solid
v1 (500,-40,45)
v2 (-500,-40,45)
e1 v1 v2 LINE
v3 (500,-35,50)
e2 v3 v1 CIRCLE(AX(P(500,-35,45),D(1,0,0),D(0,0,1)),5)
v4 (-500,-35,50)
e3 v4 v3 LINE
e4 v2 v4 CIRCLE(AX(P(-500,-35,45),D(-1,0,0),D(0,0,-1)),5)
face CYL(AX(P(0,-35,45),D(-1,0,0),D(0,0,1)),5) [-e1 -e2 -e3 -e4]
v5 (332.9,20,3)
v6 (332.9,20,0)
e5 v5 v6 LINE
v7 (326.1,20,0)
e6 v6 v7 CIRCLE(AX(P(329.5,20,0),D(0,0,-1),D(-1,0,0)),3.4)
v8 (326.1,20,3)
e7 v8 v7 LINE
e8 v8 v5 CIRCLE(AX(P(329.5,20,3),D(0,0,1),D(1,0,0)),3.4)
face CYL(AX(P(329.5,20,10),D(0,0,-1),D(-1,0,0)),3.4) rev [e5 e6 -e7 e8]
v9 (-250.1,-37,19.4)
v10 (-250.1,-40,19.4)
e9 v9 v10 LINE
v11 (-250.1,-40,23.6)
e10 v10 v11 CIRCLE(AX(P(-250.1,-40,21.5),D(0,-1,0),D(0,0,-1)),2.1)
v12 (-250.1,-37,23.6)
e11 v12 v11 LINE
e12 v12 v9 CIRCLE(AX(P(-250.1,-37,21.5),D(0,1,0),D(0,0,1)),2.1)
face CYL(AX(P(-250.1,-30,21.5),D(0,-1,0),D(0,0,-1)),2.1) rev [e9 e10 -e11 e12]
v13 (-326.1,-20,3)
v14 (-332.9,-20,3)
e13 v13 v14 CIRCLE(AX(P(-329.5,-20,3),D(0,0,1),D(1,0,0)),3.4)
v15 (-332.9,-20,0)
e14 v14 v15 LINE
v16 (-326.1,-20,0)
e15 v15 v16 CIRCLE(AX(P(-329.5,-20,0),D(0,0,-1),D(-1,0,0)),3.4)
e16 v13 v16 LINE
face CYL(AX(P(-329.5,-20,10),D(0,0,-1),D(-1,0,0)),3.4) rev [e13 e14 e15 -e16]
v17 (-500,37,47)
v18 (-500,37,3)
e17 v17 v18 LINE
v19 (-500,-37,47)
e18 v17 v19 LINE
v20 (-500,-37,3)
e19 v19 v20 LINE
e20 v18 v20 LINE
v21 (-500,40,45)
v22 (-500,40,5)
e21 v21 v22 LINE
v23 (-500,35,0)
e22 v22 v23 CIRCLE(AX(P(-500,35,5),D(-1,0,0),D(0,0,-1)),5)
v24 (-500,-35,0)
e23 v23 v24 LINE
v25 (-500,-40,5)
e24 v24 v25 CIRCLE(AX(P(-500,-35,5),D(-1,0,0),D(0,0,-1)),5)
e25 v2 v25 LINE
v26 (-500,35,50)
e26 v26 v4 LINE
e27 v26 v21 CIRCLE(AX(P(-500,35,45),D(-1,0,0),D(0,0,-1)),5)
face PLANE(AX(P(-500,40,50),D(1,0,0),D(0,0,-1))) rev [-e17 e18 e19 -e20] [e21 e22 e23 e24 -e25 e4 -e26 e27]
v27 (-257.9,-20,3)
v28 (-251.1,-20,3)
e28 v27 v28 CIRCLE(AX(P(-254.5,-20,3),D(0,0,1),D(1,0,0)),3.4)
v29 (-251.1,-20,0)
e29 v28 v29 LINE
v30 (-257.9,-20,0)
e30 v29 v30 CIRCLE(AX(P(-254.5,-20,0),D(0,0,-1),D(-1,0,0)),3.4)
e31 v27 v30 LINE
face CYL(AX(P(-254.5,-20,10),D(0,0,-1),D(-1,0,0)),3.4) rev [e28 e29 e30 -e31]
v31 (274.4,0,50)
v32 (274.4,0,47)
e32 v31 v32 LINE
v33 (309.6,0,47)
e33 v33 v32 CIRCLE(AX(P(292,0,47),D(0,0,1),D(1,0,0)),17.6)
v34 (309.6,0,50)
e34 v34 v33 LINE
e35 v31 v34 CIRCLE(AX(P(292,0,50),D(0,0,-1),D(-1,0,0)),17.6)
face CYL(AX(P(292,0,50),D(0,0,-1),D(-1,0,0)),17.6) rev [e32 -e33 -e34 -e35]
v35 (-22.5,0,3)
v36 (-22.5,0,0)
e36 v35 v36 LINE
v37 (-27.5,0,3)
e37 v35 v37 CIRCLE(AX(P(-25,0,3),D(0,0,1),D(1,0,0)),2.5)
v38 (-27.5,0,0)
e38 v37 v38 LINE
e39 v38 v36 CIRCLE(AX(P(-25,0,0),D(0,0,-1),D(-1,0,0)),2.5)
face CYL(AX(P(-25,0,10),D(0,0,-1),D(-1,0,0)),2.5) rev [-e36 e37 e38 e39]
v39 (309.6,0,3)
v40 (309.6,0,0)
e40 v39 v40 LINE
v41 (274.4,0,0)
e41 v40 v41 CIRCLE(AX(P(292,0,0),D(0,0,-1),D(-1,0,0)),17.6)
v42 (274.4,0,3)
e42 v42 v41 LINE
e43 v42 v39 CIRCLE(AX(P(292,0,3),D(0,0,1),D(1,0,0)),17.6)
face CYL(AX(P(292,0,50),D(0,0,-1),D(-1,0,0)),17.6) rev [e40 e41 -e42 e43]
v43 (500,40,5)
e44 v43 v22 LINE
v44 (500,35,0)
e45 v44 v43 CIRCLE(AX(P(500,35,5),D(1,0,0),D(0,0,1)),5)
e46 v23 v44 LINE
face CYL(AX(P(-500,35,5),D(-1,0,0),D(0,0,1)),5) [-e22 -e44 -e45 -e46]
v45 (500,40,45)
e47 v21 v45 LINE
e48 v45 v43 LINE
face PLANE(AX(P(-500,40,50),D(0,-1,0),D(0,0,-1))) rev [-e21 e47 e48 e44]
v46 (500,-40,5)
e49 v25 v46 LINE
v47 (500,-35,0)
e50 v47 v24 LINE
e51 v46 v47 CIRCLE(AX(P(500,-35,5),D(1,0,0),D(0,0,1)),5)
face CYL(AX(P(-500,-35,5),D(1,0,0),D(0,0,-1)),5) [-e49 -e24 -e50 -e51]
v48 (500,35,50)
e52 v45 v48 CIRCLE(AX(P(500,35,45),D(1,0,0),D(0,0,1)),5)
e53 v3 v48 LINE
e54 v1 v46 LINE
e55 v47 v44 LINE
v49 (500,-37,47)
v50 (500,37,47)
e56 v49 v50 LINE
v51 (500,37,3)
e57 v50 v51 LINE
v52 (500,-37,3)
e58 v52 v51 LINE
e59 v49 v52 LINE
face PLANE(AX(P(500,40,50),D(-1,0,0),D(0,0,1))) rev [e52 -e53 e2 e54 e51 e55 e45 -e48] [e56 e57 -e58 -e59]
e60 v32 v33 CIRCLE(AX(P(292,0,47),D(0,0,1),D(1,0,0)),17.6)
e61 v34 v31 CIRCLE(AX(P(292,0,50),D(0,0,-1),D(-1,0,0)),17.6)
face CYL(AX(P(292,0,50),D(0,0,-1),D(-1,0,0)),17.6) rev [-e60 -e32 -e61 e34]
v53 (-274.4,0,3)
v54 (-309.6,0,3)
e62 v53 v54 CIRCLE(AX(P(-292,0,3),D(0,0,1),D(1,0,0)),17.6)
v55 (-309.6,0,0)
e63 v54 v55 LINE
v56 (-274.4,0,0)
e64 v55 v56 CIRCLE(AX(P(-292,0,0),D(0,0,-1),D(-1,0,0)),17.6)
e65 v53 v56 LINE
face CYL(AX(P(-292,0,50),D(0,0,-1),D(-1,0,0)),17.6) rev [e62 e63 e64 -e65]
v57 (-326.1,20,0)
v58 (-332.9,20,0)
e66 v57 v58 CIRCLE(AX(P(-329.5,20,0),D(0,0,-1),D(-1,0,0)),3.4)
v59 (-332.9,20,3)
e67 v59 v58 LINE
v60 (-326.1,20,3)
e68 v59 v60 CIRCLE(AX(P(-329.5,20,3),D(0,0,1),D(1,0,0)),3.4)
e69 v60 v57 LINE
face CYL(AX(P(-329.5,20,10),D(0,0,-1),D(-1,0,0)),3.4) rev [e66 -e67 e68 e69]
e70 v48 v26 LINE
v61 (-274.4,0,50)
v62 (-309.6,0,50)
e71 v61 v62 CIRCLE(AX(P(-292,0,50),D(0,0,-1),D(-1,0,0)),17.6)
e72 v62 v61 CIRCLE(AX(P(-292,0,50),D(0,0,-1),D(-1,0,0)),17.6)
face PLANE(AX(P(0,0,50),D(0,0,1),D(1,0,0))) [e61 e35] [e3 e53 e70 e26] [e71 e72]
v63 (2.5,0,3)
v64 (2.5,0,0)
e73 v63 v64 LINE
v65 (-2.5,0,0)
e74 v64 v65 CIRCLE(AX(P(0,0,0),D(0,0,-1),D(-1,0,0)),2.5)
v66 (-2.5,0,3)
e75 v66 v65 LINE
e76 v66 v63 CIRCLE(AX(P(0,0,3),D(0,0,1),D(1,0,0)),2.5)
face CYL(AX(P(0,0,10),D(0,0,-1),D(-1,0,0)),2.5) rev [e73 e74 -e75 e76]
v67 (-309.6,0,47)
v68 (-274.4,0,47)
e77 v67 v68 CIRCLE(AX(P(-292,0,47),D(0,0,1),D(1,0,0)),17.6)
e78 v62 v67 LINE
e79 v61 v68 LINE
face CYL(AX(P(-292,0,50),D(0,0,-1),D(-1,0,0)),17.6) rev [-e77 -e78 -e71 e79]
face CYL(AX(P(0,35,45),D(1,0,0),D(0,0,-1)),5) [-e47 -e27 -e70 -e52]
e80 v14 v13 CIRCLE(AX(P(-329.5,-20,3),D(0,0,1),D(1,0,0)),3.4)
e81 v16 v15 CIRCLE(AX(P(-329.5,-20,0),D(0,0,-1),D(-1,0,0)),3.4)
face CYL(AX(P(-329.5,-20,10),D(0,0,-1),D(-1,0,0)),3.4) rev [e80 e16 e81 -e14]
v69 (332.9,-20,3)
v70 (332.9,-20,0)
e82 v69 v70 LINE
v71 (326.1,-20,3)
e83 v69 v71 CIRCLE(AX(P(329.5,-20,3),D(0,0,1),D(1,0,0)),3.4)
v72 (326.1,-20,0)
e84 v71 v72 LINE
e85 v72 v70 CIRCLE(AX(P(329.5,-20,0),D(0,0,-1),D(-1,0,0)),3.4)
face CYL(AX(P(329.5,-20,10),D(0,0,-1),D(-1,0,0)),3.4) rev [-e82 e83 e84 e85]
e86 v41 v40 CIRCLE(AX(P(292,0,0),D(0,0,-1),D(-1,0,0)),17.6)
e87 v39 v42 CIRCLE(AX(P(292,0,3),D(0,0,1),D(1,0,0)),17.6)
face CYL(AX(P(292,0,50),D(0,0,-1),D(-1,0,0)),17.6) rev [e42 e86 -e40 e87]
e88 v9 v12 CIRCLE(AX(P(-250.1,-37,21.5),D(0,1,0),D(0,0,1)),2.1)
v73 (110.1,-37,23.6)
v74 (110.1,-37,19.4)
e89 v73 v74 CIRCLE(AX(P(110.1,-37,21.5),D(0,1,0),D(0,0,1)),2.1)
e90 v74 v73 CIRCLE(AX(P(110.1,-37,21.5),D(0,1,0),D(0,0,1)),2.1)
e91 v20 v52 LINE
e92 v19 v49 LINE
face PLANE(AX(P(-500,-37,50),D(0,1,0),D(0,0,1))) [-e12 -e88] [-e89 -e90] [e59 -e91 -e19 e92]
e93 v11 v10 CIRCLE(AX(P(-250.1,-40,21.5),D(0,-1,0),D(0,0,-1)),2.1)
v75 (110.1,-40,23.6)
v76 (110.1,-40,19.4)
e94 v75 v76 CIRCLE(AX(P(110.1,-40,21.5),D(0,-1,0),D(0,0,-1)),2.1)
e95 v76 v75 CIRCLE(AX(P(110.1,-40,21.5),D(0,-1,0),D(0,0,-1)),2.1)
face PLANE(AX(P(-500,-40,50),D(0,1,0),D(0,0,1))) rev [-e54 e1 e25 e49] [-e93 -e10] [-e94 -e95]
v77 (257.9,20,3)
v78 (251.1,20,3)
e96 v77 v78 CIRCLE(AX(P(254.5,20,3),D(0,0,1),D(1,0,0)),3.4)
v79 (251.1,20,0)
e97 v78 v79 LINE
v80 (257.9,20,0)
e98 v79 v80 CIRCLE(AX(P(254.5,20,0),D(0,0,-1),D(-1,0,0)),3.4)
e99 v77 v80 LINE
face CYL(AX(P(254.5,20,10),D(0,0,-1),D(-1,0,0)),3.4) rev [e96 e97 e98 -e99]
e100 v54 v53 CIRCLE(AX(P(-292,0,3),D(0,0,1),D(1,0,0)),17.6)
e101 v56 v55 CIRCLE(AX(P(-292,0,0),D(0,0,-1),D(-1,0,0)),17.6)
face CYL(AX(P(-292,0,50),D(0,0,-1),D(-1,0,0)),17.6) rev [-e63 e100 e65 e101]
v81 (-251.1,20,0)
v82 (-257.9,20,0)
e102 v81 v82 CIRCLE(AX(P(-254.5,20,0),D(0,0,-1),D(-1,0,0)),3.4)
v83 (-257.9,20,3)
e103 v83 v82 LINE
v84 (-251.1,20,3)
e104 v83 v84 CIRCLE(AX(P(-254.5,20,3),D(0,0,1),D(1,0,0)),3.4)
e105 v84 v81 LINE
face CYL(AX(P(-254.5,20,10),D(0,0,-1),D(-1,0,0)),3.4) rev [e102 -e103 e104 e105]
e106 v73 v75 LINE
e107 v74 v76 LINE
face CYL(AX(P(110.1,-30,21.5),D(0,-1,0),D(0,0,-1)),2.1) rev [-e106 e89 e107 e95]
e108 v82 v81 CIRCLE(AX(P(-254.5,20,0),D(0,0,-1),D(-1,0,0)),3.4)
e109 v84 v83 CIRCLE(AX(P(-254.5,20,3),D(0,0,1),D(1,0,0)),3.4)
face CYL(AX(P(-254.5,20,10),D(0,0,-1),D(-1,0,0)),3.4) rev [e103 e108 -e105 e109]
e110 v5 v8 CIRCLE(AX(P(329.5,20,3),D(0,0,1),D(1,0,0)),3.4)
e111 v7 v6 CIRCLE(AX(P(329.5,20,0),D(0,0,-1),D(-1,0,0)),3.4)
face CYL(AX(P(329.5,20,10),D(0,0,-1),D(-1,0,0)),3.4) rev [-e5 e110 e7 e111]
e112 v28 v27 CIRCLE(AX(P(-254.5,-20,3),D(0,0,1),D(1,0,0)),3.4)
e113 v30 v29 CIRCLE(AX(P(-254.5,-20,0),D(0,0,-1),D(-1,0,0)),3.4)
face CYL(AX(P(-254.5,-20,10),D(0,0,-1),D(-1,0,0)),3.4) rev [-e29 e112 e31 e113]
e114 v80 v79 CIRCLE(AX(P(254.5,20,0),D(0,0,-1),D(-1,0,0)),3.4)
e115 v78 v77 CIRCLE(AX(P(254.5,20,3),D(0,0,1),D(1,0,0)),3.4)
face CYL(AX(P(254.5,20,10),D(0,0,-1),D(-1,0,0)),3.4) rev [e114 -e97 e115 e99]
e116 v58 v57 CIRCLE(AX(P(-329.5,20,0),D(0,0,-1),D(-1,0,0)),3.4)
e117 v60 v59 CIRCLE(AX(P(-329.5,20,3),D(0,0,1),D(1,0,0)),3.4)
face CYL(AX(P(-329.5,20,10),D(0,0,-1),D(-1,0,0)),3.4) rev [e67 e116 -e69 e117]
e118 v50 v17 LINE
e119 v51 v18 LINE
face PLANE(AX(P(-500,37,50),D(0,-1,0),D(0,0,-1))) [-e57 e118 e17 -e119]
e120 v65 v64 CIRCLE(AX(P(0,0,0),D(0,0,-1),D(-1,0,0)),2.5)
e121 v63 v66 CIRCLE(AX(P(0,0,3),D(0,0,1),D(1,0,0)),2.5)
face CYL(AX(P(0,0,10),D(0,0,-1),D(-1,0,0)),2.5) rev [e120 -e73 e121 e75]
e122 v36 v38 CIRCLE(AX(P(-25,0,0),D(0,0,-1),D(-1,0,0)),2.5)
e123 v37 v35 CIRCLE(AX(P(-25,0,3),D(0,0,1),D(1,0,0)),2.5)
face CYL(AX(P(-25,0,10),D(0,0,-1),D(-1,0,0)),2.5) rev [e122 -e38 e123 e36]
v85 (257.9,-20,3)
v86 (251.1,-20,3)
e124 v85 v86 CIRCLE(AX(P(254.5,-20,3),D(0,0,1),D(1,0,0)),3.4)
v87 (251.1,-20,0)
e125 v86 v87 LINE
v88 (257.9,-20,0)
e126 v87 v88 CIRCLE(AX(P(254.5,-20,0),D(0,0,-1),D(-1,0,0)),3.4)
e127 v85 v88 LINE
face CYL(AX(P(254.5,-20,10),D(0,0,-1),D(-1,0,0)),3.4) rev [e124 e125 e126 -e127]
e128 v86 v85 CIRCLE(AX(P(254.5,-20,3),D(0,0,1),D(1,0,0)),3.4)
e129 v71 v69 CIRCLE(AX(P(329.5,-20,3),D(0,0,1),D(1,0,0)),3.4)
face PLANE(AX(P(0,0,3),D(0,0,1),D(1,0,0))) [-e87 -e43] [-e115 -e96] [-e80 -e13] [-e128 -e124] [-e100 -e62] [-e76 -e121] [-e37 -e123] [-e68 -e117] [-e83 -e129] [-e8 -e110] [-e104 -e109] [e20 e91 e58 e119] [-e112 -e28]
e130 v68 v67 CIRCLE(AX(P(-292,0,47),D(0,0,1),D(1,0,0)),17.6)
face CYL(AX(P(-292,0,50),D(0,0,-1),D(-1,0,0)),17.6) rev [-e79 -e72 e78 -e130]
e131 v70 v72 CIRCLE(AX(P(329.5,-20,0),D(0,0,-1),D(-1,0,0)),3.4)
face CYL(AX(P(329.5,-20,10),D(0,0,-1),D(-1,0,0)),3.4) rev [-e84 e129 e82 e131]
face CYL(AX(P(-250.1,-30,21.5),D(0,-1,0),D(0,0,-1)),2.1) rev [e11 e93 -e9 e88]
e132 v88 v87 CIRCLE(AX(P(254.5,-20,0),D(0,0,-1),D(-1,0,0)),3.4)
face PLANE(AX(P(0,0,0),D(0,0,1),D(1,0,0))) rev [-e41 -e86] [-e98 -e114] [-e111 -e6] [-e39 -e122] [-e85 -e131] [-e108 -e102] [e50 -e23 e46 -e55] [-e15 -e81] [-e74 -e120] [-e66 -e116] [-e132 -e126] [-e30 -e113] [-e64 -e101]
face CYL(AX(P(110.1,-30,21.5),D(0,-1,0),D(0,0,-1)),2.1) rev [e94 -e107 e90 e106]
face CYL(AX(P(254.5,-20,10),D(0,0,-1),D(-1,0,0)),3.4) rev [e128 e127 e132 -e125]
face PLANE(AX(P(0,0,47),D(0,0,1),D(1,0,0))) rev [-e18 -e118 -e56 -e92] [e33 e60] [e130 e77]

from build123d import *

# Parameters (mm, degrees)
SKETCH_1_W          = 1000
SKETCH_1_H          = 80
EXTRUDE_1_DEPTH     = 50
SHELL_1_T           = -3
FILLET_1_R          = 5
SKETCH_3_R          = 17.6
CUT_EXTRUDE_2_DEPTH = 505.083326445
SKETCH_4_R          = 3.4
CUT_EXTRUDE_3_DEPTH = 10
SKETCH_5_R          = 2.5
CUT_EXTRUDE_4_DEPTH = 10
SKETCH_6_R          = 2.1
CUT_EXTRUDE_5_DEPTH = 10


with BuildPart() as part:
    # 草图1 → 凸台-拉伸1 (new body)
    with BuildSketch(Plane.XY):
        Rectangle(SKETCH_1_W, SKETCH_1_H)
    extrude(amount=EXTRUDE_1_DEPTH)

    # 抽壳1
    shell_1_openings = [part.faces().sort_by_distance(p)[0] for p in [
        (-500, 0, 25),
        (500, 0, 25),
    ]]
    offset(amount=SHELL_1_T, openings=shell_1_openings, kind=Kind.INTERSECTION)

    # 圆角1
    fillet_1_edges = [part.edges().sort_by_distance(p)[0] for p in [
        (0, -40, 50),
        (0, -40, 0),
        (0, 40, 0),
        (0, 40, 50),
    ]]
    fillet(fillet_1_edges, radius=FILLET_1_R)

    # 草图3 → 切除-拉伸2 (cut, through all)
    with BuildSketch(Plane(origin=(0, 0, 0), x_dir=(-1, 0, 0), z_dir=(0, 0, -1))):
        with Locations((-292, 0)):
            Circle(SKETCH_3_R)
        with Locations((292, 0)):
            Circle(SKETCH_3_R)
    extrude(amount=-CUT_EXTRUDE_2_DEPTH, mode=Mode.SUBTRACT)

    # 草图4 → 切除-拉伸3 (cut)
    with BuildSketch(Plane(origin=(0, 0, 0), x_dir=(-1, 0, 0), z_dir=(0, 0, -1))):
        with Locations((-329.5, 20)):
            Circle(SKETCH_4_R)
        with Locations((-329.5, -20)):
            Circle(SKETCH_4_R)
        with Locations((-254.5, 20)):
            Circle(SKETCH_4_R)
        with Locations((-254.5, -20)):
            Circle(SKETCH_4_R)
        with Locations((254.5, 20)):
            Circle(SKETCH_4_R)
        with Locations((254.5, -20)):
            Circle(SKETCH_4_R)
        with Locations((329.5, 20)):
            Circle(SKETCH_4_R)
        with Locations((329.5, -20)):
            Circle(SKETCH_4_R)
    extrude(amount=-CUT_EXTRUDE_3_DEPTH, mode=Mode.SUBTRACT)

    # 草图5 → 切除-拉伸4 (cut)
    with BuildSketch(Plane(origin=(0, 0, 0), x_dir=(-1, 0, 0), z_dir=(0, 0, -1))):
        Circle(SKETCH_5_R)
        with Locations((25, 0)):
            Circle(SKETCH_5_R)
    extrude(amount=-CUT_EXTRUDE_4_DEPTH, mode=Mode.SUBTRACT)

    # 草图6 → 切除-拉伸5 (cut)
    with BuildSketch(Plane.XZ.offset(40)):
        with Locations(Location((110.1, 21.5, 0), (0, 0, 270))):
            Circle(SKETCH_6_R)
        with Locations(Location((-250.1, 21.5, 0), (0, 0, 270))):
            Circle(SKETCH_6_R)
    extrude(amount=-CUT_EXTRUDE_5_DEPTH, mode=Mode.SUBTRACT)


solid = part.part
